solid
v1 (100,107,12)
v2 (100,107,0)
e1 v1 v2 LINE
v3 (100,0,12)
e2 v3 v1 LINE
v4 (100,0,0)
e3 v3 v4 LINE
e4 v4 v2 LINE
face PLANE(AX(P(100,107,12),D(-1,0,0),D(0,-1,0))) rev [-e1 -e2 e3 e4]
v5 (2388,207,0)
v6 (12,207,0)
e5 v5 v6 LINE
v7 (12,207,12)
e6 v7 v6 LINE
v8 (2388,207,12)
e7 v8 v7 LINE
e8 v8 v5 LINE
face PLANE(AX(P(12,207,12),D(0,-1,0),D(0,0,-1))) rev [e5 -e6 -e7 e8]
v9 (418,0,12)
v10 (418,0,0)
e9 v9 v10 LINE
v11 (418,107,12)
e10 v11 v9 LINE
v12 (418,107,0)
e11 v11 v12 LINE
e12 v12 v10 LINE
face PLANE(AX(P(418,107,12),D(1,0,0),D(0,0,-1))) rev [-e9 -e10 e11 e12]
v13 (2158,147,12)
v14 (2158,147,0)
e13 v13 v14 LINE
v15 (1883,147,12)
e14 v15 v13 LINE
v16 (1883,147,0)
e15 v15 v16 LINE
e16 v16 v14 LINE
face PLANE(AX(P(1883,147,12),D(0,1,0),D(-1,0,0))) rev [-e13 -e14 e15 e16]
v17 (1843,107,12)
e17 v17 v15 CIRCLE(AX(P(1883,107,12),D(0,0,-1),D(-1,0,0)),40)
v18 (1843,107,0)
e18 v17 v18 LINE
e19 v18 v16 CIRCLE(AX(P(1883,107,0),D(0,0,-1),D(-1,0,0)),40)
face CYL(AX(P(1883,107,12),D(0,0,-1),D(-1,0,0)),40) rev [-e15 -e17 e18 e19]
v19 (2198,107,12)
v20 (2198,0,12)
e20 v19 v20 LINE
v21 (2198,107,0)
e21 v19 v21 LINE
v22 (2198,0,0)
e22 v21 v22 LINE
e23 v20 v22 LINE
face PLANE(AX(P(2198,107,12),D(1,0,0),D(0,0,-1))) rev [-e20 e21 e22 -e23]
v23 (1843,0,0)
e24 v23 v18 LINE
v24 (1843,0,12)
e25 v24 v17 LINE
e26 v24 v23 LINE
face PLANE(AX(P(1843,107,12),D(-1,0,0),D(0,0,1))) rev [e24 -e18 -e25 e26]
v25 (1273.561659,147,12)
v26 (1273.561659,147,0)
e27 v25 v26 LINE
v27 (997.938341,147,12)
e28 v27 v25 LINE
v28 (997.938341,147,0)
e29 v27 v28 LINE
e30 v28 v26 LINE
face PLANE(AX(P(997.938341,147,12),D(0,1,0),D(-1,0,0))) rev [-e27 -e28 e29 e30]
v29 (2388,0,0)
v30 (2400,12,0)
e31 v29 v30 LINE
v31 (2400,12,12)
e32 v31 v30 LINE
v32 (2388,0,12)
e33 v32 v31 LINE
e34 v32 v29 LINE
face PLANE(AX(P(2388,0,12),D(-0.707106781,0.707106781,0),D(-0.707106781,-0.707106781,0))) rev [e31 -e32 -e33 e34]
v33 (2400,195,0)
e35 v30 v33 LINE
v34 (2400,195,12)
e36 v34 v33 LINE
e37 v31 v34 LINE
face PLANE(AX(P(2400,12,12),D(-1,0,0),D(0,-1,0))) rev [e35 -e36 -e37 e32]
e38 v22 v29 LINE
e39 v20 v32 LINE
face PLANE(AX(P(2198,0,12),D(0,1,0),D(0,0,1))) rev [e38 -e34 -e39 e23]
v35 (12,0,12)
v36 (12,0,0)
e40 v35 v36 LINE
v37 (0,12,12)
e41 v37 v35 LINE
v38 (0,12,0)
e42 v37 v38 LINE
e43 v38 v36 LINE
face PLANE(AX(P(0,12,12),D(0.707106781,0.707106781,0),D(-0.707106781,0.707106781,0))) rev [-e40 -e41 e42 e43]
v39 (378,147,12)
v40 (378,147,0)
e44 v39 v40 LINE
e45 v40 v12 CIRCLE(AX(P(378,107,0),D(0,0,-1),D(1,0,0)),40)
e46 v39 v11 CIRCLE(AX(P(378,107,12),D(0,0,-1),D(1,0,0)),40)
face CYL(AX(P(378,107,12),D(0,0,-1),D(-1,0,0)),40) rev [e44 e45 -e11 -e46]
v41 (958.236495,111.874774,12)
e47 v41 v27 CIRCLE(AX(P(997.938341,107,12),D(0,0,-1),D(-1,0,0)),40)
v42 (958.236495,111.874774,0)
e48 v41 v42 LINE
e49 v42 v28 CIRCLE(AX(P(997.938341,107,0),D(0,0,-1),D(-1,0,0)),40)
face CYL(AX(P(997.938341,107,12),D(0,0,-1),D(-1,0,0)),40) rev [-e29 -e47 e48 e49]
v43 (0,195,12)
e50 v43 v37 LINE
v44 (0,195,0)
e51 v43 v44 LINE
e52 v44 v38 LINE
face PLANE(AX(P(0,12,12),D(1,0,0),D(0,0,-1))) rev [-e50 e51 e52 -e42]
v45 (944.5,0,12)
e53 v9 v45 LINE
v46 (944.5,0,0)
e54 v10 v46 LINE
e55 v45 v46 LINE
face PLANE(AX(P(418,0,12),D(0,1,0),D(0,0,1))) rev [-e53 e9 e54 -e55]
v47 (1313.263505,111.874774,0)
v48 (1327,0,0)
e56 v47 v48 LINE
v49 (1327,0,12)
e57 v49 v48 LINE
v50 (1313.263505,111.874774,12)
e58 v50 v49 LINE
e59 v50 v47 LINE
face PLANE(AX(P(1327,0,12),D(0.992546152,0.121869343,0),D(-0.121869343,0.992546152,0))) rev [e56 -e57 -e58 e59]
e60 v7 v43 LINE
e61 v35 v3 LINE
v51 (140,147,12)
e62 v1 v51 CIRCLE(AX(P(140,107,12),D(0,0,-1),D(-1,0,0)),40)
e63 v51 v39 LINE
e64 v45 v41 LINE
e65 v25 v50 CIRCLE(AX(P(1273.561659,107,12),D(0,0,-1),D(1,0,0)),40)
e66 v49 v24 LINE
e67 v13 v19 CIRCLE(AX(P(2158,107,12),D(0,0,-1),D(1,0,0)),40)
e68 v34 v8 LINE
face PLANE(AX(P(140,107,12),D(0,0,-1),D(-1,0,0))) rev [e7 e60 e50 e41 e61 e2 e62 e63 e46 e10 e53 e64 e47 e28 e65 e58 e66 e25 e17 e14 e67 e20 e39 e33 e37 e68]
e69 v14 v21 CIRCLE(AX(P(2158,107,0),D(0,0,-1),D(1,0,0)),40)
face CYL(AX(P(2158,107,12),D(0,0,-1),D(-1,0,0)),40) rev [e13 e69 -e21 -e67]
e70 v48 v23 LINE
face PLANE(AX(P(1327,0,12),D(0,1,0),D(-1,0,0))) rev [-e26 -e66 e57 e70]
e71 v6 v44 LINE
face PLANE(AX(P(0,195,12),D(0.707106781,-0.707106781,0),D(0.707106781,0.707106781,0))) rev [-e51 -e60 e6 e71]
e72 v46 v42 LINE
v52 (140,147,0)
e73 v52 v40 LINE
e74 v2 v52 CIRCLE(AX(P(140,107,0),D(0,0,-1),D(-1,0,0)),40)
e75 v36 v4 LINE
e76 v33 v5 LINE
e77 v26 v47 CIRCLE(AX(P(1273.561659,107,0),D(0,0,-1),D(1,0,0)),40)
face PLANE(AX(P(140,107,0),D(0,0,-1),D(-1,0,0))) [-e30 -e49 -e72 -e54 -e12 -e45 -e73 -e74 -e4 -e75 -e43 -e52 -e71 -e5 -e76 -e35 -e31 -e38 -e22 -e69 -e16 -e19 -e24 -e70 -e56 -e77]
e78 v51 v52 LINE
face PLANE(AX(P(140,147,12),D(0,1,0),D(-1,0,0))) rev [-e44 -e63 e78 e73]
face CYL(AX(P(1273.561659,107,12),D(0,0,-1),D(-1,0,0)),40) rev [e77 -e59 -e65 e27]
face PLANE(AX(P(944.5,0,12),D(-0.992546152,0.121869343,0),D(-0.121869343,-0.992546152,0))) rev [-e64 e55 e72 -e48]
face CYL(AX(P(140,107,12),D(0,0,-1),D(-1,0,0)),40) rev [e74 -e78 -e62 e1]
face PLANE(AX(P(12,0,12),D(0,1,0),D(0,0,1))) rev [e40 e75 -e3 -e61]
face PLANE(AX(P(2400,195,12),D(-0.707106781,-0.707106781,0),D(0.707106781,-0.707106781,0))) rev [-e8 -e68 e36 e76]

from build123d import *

# Parameters (mm, degrees)
BOSS_EXTRUDE1_DEPTH = 12


with BuildPart() as part:
    # Sketch1 → Boss-Extrude1 (new body)
    with BuildSketch(Plane.XY):
        with BuildLine():
            Line((140, 147), (378, 147))
            ThreePointArc((378, 147), (406.284271247, 135.284271247), (418, 107))
            Line((418, 107), (418, 0))
            Line((418, 0), (944.5, 0))
            Line((944.5, 0), (958.236494969, 111.874773736))
            ThreePointArc((958.236494969, 111.874773736), (971.433539106, 136.958228832), (997.938341035, 147))
            Line((997.938341035, 147), (1273.561658965, 147))
            ThreePointArc((1273.561658965, 147), (1300.066460894, 136.958228832), (1313.263505031, 111.874773736))
            Line((1313.263505031, 111.874773736), (1327, 0))
            Line((1327, 0), (1843, 0))
            Line((1843, 0), (1843, 107))
            ThreePointArc((1843, 107), (1854.715728753, 135.284271247), (1883, 147))
            Line((1883, 147), (2158, 147))
            ThreePointArc((2158, 147), (2186.284271247, 135.284271247), (2198, 107))
            Line((2198, 107), (2198, 0))
            Line((2198, 0), (2388, 0))
            Line((2388, 0), (2400, 12))
            Line((2400, 12), (2400, 195))
            Line((2400, 195), (2388, 207))
            Line((2388, 207), (12, 207))
            Line((12, 207), (0, 195))
            Line((0, 195), (0, 12))
            Line((0, 12), (12, 0))
            Line((12, 0), (100, 0))
            Line((100, 0), (100, 107))
            ThreePointArc((100, 107), (111.715728753, 135.284271247), (140, 147))
        make_face()
    extrude(amount=BOSS_EXTRUDE1_DEPTH)


solid = part.part
